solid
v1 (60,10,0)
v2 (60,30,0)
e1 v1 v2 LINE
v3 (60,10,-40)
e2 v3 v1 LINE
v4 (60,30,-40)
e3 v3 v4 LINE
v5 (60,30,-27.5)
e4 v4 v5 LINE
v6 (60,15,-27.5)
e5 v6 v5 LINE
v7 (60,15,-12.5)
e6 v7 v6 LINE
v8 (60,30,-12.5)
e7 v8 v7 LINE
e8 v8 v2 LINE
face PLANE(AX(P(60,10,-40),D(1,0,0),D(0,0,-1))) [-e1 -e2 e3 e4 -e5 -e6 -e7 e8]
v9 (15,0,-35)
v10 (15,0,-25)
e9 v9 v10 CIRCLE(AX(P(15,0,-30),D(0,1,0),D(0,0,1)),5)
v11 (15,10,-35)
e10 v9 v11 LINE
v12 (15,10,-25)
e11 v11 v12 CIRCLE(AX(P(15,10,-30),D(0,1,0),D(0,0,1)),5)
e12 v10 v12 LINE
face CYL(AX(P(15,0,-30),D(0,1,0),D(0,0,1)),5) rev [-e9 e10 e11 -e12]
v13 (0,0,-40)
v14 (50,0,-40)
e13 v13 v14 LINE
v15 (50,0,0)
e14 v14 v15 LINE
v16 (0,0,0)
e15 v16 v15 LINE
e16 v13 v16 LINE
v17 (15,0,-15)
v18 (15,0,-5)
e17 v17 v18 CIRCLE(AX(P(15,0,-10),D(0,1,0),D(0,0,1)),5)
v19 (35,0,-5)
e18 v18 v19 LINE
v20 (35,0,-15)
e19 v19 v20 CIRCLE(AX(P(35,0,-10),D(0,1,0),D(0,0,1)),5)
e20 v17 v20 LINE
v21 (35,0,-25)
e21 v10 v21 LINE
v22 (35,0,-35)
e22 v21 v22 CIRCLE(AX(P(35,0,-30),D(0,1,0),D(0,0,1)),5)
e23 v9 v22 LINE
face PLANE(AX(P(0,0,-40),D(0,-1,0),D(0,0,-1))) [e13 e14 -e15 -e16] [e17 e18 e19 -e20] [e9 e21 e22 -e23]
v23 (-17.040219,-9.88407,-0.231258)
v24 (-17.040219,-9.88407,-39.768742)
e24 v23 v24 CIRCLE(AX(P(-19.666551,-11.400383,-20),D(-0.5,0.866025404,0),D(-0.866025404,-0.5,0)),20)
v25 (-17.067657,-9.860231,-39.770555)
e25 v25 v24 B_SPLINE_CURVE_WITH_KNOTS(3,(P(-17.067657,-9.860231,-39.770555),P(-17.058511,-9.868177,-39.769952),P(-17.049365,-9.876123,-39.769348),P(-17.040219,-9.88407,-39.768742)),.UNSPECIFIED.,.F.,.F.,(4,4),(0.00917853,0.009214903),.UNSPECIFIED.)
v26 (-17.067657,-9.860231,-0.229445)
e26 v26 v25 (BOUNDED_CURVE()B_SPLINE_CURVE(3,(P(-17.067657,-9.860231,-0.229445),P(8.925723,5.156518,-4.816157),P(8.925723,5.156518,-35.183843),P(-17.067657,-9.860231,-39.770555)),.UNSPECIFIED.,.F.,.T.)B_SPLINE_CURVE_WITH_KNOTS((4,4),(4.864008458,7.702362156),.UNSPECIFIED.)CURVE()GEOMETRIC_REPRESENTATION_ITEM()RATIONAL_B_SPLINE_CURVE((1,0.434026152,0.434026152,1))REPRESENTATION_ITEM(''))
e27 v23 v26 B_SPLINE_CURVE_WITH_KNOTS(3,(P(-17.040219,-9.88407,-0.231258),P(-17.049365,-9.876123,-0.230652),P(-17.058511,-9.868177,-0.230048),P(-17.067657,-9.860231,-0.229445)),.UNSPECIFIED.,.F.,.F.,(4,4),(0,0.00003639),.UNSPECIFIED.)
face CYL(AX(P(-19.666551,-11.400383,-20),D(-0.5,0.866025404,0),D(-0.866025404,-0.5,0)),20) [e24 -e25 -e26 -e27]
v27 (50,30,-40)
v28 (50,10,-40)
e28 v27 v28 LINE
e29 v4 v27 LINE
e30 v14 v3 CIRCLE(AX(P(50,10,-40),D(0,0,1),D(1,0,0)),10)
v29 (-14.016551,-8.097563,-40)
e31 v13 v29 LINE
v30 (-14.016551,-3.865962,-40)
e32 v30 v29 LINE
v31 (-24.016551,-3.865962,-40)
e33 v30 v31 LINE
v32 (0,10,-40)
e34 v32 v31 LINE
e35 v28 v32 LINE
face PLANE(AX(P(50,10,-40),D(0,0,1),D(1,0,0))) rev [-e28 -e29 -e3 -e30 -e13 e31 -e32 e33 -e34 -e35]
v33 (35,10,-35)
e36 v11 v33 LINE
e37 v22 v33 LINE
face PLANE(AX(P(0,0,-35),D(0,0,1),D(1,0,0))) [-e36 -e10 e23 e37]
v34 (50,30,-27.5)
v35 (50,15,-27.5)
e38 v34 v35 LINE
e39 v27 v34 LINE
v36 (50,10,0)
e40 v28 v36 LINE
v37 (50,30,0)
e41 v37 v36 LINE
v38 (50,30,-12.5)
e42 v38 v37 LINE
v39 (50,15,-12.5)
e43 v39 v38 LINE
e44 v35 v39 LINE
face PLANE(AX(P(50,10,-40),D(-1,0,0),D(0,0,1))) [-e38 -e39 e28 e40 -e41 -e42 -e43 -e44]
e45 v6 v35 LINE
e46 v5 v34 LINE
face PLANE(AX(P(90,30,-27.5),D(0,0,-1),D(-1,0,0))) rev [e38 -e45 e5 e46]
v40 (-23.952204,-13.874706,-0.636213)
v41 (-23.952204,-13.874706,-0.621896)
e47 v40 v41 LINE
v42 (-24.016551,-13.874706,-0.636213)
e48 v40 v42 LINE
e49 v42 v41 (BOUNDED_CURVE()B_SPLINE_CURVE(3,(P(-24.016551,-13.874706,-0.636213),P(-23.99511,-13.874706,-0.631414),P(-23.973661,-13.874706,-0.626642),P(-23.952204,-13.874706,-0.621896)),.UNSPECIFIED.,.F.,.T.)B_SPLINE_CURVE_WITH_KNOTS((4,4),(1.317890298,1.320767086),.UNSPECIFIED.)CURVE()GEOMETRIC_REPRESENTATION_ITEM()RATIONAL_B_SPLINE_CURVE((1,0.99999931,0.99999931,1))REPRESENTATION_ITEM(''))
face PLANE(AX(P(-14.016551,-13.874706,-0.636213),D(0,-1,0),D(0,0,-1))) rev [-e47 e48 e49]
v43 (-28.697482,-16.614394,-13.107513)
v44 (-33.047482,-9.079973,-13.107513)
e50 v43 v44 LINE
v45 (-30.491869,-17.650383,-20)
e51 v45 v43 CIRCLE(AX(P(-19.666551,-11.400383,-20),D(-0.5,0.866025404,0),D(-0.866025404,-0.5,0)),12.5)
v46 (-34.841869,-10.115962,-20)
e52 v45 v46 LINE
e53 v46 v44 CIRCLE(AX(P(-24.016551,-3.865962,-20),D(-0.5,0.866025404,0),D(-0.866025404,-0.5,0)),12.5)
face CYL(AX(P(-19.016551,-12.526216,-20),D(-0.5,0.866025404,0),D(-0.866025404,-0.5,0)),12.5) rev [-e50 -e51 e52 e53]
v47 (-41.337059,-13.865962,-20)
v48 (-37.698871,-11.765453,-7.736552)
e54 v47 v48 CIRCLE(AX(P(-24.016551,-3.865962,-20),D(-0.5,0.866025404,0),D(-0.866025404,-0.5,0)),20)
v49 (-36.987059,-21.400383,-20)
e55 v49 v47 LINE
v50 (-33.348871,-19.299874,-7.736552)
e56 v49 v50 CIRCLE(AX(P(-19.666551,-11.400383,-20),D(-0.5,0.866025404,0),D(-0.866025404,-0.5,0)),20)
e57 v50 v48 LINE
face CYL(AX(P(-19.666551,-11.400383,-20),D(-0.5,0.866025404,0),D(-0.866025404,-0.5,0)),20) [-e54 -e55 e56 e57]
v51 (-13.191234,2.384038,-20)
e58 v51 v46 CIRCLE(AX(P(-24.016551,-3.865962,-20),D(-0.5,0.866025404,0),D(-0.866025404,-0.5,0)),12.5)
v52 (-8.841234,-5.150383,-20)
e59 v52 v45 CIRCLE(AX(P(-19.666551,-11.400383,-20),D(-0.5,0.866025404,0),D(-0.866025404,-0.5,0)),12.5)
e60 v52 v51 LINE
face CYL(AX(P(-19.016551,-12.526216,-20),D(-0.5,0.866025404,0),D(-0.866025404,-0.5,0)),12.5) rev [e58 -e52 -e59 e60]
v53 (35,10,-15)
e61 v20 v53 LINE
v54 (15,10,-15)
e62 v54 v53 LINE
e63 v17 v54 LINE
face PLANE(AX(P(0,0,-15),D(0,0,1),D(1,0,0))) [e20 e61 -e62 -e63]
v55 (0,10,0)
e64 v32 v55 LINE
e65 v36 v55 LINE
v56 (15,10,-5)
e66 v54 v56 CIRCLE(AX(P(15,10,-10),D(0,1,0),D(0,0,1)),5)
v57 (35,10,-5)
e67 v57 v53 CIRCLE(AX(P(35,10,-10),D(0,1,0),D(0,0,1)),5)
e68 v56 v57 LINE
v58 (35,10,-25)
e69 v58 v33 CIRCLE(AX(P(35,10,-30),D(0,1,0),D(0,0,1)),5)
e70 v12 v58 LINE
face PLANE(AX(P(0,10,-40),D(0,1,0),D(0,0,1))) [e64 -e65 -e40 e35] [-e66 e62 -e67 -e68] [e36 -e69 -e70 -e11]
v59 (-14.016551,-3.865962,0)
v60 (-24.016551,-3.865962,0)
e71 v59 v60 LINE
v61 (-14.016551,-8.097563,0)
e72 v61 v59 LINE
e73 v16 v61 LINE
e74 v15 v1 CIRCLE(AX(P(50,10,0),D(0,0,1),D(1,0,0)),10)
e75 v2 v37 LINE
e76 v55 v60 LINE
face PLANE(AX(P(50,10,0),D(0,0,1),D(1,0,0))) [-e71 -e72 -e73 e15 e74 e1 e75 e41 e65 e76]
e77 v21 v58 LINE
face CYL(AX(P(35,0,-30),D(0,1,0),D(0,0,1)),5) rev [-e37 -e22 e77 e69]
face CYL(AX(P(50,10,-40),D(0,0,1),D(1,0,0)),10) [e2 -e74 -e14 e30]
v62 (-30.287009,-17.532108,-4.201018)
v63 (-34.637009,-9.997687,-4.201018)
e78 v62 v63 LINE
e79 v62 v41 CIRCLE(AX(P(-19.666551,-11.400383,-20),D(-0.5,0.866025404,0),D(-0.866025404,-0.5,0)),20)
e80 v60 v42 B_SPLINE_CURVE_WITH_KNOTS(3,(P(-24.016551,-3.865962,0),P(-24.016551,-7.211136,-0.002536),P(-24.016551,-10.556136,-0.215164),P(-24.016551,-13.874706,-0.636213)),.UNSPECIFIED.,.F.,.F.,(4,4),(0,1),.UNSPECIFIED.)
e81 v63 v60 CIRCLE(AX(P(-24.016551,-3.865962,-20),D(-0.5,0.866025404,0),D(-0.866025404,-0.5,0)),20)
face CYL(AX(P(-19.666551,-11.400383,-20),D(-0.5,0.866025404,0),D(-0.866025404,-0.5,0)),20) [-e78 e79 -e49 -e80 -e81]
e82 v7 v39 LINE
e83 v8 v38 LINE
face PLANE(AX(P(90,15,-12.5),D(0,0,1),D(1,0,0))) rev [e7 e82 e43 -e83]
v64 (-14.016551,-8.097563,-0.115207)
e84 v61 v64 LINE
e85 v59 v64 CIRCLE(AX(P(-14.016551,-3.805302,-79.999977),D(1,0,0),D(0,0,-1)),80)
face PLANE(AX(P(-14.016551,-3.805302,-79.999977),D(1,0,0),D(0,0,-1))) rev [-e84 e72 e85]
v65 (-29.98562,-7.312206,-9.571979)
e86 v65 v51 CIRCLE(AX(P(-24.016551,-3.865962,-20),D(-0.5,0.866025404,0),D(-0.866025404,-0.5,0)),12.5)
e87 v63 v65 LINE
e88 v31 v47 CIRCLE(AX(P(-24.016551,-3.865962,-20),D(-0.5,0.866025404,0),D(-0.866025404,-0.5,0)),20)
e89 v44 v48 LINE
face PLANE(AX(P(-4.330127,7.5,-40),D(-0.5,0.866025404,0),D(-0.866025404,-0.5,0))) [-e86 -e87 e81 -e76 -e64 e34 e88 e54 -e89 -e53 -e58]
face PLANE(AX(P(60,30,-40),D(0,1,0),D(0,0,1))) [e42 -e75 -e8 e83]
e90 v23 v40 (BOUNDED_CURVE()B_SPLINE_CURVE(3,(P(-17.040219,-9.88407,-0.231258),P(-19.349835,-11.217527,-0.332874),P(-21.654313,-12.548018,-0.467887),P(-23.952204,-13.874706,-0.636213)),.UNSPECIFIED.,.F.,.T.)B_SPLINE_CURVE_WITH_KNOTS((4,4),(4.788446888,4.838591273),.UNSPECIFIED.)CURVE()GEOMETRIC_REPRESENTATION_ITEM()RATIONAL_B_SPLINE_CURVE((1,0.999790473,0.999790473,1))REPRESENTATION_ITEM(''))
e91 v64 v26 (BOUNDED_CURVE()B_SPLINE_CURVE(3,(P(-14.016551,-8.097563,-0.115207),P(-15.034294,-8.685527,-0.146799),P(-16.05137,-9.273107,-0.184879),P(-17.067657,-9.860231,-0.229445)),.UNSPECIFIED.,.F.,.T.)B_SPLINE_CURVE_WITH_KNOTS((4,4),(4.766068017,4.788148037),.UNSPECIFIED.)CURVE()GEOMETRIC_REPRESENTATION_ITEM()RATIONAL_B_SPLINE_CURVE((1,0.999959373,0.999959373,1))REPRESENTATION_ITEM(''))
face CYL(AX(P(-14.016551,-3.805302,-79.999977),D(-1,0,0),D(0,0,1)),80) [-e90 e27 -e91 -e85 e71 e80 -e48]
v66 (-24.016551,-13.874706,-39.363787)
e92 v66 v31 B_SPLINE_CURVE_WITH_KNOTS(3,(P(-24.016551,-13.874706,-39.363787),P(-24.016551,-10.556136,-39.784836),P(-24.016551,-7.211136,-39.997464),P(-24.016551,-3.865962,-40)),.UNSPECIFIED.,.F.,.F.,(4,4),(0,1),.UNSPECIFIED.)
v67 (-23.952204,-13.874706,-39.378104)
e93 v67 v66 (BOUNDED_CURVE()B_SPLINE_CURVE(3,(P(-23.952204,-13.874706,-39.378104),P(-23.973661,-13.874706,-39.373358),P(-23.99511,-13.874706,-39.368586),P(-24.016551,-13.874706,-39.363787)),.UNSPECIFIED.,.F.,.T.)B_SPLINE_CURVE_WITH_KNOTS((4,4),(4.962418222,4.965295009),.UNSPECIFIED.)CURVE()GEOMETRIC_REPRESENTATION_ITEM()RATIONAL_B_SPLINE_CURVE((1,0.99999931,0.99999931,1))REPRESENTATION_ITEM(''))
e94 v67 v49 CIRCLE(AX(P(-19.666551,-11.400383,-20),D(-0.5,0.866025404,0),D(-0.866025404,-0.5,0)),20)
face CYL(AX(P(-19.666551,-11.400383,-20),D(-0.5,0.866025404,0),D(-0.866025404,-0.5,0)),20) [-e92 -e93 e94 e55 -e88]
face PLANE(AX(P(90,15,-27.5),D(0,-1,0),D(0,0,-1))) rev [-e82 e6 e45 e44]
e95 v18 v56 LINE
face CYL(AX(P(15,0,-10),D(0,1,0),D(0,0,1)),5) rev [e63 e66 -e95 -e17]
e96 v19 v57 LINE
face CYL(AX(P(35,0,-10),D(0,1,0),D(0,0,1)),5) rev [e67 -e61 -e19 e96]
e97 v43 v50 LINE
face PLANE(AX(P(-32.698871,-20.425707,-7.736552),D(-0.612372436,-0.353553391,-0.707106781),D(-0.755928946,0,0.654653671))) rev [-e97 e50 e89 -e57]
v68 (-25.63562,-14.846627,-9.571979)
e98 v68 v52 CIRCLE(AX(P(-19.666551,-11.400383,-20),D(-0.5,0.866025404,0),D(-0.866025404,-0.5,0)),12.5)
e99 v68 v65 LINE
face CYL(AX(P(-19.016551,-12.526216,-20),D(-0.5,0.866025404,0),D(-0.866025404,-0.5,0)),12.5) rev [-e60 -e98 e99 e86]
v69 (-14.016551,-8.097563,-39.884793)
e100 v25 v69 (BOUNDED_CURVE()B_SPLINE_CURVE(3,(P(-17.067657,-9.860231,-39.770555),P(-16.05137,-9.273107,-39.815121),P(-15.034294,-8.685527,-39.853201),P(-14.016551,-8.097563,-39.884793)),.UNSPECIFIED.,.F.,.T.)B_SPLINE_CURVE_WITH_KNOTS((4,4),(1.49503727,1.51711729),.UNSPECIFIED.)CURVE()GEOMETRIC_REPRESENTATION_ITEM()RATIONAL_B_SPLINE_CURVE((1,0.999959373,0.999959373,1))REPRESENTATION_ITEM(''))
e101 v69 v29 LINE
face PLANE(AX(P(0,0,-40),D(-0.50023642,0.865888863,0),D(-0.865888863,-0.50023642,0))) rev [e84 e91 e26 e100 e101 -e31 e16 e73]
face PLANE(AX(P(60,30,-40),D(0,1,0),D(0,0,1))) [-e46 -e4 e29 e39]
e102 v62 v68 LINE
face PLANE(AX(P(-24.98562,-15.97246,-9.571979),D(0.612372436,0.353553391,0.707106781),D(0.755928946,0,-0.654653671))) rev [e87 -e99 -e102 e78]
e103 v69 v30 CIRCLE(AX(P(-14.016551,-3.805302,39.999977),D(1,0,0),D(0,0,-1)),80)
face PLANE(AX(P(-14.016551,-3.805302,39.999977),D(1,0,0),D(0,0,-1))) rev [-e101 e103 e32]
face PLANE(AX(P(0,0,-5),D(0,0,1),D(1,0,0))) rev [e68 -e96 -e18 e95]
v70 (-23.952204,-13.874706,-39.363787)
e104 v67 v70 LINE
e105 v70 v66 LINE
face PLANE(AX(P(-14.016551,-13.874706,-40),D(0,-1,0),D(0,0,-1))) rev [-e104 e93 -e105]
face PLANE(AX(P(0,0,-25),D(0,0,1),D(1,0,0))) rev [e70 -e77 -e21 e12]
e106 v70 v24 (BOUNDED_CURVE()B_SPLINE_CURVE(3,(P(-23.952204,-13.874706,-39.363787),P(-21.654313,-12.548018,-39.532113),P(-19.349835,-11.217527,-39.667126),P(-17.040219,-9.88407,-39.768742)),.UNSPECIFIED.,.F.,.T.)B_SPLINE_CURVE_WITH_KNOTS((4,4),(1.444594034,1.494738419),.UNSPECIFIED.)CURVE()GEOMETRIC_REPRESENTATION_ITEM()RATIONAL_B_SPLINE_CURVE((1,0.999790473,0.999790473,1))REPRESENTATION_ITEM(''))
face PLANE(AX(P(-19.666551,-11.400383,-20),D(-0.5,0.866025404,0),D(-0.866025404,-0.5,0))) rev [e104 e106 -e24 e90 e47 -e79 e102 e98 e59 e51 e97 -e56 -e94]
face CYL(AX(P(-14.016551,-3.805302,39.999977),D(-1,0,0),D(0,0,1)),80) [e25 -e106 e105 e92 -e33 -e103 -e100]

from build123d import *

# Parameters (mm, degrees)
L_BRACKET_BASE_DEPTH  = 40
CORNER_NOTCH_SKETCH_W = 15
CORNER_NOTCH_SKETCH_H = 15
CORNER_NOTCH_DEPTH    = 40
ANGLED_EYE_ARM_DEPTH  = 40
EYE_PAD_SKETCH_R      = 20
EYE_PAD_DEPTH         = 8.7
SLOT_1_DEPTH          = 10
SLOT_2_DEPTH          = 10
SPLIT_EYE_CUT_DEPTH   = 10
U_FORK_CUT_DEPTH      = 10


with BuildPart() as part:
    # L-Profile Sketch → L-Bracket Base (new body)
    with BuildSketch(Plane.XY):
        with BuildLine():
            Line((0, 0), (50, 0))
            ThreePointArc((50, 0), (57.071067812, 2.928932188), (60, 10))
            Line((60, 10), (60, 30))
            Line((60, 30), (50, 30))
            Line((50, 30), (50, 10))
            Line((50, 10), (0, 10))
            Line((0, 10), (0, 0))
        make_face()
    extrude(amount=-L_BRACKET_BASE_DEPTH)

    # Corner Notch Sketch → Corner Notch (cut)
    with BuildSketch(Plane.ZY.offset(-50)):
        with Locations((-20, 22.5)):
            Rectangle(CORNER_NOTCH_SKETCH_W, CORNER_NOTCH_SKETCH_H)
    extrude(amount=-CORNER_NOTCH_DEPTH, mode=Mode.SUBTRACT)

    # Angled Arm Sketch 60deg → Angled Eye Arm (add)
    with BuildSketch(Plane.XY):
        Polygon((-24.016551345, -13.87470631), (-24.016551345, -3.865962384), (0, 10), (0, 0), align=None)
    extrude(amount=-ANGLED_EYE_ARM_DEPTH)

    # Eye Pad Sketch → Eye Pad (add)
    with BuildSketch(Plane(origin=(-4.330127019, 7.5, 0), x_dir=(0.8660254037844397, 0.4999999999999981, 0), z_dir=(-0.4999999999999982, 0.8660254037844398, 0))):
        with Locations(Location((-22.731924769, 20, 0), (0, 0, 180))):
            Circle(EYE_PAD_SKETCH_R)
    extrude(amount=-EYE_PAD_DEPTH)

    # Slot 1 Sketch → Slot 1 (cut)
    with BuildSketch(Plane.ZY.offset(24.016551345)):
        with BuildLine():
            Line((-0.636212631, -13.87470631), (0, -13.87470631))
            Line((0, -13.87470631), (0, -3.865962384))
            ThreePointArc((0, -3.865962384), (-0.161112689, -8.880313754), (-0.636212631, -13.87470631))
        make_face()
    extrude(amount=-SLOT_1_DEPTH, mode=Mode.SUBTRACT)

    # Slot 2 Sketch → Slot 2 (cut)
    with BuildSketch(Plane.ZY.offset(24.016551345)):
        with BuildLine():
            Line((-40, -13.87470631), (-40, -3.865962384))
            ThreePointArc((-40, -3.865962384), (-39.838887311, -8.880313754), (-39.363787369, -13.87470631))
            Line((-39.363787369, -13.87470631), (-40, -13.87470631))
        make_face()
    extrude(amount=-SLOT_2_DEPTH, mode=Mode.SUBTRACT)

    # Split Eye Sketch → Split Eye Cut (cut)
    with BuildSketch(Plane(origin=(-4.330127019, 7.5, 0), x_dir=(0.8660254037844397, 0.4999999999999981, 0), z_dir=(-0.4999999999999982, 0.8660254037844398, 0))):
        with BuildLine():
            Line((-38.530906922, 7.736551753), (-33.159945759, 13.107512915))
            ThreePointArc((-33.159945759, 13.107512915), (-13.893090004, 28.838834765), (-29.624411853, 9.571979009))
            Line((-29.624411853, 9.571979009), (-34.995373016, 4.201017847))
            ThreePointArc((-34.995373016, 4.201017847), (-36.874060392, 5.857864376), (-38.530906922, 7.736551753))
        make_face()
    extrude(amount=-SPLIT_EYE_CUT_DEPTH, mode=Mode.SUBTRACT)

    # U-Fork Sketch → U-Fork Cut (cut)
    with BuildSketch(Plane(origin=(0, 10, 0), x_dir=(1, 0, 0), z_dir=(0, 1, 0))):
        with BuildLine():
            Line((15, 25), (35, 25))
            ThreePointArc((35, 25), (40, 30), (35, 35))
            Line((35, 35), (15, 35))
            ThreePointArc((15, 35), (10, 30), (15, 25))
        make_face()
        with BuildLine():
            Line((15, 5), (35, 5))
            ThreePointArc((35, 5), (40, 10), (35, 15))
            Line((35, 15), (15, 15))
            ThreePointArc((15, 15), (10, 10), (15, 5))
        make_face()
    extrude(amount=-U_FORK_CUT_DEPTH, mode=Mode.SUBTRACT)


solid = part.part
